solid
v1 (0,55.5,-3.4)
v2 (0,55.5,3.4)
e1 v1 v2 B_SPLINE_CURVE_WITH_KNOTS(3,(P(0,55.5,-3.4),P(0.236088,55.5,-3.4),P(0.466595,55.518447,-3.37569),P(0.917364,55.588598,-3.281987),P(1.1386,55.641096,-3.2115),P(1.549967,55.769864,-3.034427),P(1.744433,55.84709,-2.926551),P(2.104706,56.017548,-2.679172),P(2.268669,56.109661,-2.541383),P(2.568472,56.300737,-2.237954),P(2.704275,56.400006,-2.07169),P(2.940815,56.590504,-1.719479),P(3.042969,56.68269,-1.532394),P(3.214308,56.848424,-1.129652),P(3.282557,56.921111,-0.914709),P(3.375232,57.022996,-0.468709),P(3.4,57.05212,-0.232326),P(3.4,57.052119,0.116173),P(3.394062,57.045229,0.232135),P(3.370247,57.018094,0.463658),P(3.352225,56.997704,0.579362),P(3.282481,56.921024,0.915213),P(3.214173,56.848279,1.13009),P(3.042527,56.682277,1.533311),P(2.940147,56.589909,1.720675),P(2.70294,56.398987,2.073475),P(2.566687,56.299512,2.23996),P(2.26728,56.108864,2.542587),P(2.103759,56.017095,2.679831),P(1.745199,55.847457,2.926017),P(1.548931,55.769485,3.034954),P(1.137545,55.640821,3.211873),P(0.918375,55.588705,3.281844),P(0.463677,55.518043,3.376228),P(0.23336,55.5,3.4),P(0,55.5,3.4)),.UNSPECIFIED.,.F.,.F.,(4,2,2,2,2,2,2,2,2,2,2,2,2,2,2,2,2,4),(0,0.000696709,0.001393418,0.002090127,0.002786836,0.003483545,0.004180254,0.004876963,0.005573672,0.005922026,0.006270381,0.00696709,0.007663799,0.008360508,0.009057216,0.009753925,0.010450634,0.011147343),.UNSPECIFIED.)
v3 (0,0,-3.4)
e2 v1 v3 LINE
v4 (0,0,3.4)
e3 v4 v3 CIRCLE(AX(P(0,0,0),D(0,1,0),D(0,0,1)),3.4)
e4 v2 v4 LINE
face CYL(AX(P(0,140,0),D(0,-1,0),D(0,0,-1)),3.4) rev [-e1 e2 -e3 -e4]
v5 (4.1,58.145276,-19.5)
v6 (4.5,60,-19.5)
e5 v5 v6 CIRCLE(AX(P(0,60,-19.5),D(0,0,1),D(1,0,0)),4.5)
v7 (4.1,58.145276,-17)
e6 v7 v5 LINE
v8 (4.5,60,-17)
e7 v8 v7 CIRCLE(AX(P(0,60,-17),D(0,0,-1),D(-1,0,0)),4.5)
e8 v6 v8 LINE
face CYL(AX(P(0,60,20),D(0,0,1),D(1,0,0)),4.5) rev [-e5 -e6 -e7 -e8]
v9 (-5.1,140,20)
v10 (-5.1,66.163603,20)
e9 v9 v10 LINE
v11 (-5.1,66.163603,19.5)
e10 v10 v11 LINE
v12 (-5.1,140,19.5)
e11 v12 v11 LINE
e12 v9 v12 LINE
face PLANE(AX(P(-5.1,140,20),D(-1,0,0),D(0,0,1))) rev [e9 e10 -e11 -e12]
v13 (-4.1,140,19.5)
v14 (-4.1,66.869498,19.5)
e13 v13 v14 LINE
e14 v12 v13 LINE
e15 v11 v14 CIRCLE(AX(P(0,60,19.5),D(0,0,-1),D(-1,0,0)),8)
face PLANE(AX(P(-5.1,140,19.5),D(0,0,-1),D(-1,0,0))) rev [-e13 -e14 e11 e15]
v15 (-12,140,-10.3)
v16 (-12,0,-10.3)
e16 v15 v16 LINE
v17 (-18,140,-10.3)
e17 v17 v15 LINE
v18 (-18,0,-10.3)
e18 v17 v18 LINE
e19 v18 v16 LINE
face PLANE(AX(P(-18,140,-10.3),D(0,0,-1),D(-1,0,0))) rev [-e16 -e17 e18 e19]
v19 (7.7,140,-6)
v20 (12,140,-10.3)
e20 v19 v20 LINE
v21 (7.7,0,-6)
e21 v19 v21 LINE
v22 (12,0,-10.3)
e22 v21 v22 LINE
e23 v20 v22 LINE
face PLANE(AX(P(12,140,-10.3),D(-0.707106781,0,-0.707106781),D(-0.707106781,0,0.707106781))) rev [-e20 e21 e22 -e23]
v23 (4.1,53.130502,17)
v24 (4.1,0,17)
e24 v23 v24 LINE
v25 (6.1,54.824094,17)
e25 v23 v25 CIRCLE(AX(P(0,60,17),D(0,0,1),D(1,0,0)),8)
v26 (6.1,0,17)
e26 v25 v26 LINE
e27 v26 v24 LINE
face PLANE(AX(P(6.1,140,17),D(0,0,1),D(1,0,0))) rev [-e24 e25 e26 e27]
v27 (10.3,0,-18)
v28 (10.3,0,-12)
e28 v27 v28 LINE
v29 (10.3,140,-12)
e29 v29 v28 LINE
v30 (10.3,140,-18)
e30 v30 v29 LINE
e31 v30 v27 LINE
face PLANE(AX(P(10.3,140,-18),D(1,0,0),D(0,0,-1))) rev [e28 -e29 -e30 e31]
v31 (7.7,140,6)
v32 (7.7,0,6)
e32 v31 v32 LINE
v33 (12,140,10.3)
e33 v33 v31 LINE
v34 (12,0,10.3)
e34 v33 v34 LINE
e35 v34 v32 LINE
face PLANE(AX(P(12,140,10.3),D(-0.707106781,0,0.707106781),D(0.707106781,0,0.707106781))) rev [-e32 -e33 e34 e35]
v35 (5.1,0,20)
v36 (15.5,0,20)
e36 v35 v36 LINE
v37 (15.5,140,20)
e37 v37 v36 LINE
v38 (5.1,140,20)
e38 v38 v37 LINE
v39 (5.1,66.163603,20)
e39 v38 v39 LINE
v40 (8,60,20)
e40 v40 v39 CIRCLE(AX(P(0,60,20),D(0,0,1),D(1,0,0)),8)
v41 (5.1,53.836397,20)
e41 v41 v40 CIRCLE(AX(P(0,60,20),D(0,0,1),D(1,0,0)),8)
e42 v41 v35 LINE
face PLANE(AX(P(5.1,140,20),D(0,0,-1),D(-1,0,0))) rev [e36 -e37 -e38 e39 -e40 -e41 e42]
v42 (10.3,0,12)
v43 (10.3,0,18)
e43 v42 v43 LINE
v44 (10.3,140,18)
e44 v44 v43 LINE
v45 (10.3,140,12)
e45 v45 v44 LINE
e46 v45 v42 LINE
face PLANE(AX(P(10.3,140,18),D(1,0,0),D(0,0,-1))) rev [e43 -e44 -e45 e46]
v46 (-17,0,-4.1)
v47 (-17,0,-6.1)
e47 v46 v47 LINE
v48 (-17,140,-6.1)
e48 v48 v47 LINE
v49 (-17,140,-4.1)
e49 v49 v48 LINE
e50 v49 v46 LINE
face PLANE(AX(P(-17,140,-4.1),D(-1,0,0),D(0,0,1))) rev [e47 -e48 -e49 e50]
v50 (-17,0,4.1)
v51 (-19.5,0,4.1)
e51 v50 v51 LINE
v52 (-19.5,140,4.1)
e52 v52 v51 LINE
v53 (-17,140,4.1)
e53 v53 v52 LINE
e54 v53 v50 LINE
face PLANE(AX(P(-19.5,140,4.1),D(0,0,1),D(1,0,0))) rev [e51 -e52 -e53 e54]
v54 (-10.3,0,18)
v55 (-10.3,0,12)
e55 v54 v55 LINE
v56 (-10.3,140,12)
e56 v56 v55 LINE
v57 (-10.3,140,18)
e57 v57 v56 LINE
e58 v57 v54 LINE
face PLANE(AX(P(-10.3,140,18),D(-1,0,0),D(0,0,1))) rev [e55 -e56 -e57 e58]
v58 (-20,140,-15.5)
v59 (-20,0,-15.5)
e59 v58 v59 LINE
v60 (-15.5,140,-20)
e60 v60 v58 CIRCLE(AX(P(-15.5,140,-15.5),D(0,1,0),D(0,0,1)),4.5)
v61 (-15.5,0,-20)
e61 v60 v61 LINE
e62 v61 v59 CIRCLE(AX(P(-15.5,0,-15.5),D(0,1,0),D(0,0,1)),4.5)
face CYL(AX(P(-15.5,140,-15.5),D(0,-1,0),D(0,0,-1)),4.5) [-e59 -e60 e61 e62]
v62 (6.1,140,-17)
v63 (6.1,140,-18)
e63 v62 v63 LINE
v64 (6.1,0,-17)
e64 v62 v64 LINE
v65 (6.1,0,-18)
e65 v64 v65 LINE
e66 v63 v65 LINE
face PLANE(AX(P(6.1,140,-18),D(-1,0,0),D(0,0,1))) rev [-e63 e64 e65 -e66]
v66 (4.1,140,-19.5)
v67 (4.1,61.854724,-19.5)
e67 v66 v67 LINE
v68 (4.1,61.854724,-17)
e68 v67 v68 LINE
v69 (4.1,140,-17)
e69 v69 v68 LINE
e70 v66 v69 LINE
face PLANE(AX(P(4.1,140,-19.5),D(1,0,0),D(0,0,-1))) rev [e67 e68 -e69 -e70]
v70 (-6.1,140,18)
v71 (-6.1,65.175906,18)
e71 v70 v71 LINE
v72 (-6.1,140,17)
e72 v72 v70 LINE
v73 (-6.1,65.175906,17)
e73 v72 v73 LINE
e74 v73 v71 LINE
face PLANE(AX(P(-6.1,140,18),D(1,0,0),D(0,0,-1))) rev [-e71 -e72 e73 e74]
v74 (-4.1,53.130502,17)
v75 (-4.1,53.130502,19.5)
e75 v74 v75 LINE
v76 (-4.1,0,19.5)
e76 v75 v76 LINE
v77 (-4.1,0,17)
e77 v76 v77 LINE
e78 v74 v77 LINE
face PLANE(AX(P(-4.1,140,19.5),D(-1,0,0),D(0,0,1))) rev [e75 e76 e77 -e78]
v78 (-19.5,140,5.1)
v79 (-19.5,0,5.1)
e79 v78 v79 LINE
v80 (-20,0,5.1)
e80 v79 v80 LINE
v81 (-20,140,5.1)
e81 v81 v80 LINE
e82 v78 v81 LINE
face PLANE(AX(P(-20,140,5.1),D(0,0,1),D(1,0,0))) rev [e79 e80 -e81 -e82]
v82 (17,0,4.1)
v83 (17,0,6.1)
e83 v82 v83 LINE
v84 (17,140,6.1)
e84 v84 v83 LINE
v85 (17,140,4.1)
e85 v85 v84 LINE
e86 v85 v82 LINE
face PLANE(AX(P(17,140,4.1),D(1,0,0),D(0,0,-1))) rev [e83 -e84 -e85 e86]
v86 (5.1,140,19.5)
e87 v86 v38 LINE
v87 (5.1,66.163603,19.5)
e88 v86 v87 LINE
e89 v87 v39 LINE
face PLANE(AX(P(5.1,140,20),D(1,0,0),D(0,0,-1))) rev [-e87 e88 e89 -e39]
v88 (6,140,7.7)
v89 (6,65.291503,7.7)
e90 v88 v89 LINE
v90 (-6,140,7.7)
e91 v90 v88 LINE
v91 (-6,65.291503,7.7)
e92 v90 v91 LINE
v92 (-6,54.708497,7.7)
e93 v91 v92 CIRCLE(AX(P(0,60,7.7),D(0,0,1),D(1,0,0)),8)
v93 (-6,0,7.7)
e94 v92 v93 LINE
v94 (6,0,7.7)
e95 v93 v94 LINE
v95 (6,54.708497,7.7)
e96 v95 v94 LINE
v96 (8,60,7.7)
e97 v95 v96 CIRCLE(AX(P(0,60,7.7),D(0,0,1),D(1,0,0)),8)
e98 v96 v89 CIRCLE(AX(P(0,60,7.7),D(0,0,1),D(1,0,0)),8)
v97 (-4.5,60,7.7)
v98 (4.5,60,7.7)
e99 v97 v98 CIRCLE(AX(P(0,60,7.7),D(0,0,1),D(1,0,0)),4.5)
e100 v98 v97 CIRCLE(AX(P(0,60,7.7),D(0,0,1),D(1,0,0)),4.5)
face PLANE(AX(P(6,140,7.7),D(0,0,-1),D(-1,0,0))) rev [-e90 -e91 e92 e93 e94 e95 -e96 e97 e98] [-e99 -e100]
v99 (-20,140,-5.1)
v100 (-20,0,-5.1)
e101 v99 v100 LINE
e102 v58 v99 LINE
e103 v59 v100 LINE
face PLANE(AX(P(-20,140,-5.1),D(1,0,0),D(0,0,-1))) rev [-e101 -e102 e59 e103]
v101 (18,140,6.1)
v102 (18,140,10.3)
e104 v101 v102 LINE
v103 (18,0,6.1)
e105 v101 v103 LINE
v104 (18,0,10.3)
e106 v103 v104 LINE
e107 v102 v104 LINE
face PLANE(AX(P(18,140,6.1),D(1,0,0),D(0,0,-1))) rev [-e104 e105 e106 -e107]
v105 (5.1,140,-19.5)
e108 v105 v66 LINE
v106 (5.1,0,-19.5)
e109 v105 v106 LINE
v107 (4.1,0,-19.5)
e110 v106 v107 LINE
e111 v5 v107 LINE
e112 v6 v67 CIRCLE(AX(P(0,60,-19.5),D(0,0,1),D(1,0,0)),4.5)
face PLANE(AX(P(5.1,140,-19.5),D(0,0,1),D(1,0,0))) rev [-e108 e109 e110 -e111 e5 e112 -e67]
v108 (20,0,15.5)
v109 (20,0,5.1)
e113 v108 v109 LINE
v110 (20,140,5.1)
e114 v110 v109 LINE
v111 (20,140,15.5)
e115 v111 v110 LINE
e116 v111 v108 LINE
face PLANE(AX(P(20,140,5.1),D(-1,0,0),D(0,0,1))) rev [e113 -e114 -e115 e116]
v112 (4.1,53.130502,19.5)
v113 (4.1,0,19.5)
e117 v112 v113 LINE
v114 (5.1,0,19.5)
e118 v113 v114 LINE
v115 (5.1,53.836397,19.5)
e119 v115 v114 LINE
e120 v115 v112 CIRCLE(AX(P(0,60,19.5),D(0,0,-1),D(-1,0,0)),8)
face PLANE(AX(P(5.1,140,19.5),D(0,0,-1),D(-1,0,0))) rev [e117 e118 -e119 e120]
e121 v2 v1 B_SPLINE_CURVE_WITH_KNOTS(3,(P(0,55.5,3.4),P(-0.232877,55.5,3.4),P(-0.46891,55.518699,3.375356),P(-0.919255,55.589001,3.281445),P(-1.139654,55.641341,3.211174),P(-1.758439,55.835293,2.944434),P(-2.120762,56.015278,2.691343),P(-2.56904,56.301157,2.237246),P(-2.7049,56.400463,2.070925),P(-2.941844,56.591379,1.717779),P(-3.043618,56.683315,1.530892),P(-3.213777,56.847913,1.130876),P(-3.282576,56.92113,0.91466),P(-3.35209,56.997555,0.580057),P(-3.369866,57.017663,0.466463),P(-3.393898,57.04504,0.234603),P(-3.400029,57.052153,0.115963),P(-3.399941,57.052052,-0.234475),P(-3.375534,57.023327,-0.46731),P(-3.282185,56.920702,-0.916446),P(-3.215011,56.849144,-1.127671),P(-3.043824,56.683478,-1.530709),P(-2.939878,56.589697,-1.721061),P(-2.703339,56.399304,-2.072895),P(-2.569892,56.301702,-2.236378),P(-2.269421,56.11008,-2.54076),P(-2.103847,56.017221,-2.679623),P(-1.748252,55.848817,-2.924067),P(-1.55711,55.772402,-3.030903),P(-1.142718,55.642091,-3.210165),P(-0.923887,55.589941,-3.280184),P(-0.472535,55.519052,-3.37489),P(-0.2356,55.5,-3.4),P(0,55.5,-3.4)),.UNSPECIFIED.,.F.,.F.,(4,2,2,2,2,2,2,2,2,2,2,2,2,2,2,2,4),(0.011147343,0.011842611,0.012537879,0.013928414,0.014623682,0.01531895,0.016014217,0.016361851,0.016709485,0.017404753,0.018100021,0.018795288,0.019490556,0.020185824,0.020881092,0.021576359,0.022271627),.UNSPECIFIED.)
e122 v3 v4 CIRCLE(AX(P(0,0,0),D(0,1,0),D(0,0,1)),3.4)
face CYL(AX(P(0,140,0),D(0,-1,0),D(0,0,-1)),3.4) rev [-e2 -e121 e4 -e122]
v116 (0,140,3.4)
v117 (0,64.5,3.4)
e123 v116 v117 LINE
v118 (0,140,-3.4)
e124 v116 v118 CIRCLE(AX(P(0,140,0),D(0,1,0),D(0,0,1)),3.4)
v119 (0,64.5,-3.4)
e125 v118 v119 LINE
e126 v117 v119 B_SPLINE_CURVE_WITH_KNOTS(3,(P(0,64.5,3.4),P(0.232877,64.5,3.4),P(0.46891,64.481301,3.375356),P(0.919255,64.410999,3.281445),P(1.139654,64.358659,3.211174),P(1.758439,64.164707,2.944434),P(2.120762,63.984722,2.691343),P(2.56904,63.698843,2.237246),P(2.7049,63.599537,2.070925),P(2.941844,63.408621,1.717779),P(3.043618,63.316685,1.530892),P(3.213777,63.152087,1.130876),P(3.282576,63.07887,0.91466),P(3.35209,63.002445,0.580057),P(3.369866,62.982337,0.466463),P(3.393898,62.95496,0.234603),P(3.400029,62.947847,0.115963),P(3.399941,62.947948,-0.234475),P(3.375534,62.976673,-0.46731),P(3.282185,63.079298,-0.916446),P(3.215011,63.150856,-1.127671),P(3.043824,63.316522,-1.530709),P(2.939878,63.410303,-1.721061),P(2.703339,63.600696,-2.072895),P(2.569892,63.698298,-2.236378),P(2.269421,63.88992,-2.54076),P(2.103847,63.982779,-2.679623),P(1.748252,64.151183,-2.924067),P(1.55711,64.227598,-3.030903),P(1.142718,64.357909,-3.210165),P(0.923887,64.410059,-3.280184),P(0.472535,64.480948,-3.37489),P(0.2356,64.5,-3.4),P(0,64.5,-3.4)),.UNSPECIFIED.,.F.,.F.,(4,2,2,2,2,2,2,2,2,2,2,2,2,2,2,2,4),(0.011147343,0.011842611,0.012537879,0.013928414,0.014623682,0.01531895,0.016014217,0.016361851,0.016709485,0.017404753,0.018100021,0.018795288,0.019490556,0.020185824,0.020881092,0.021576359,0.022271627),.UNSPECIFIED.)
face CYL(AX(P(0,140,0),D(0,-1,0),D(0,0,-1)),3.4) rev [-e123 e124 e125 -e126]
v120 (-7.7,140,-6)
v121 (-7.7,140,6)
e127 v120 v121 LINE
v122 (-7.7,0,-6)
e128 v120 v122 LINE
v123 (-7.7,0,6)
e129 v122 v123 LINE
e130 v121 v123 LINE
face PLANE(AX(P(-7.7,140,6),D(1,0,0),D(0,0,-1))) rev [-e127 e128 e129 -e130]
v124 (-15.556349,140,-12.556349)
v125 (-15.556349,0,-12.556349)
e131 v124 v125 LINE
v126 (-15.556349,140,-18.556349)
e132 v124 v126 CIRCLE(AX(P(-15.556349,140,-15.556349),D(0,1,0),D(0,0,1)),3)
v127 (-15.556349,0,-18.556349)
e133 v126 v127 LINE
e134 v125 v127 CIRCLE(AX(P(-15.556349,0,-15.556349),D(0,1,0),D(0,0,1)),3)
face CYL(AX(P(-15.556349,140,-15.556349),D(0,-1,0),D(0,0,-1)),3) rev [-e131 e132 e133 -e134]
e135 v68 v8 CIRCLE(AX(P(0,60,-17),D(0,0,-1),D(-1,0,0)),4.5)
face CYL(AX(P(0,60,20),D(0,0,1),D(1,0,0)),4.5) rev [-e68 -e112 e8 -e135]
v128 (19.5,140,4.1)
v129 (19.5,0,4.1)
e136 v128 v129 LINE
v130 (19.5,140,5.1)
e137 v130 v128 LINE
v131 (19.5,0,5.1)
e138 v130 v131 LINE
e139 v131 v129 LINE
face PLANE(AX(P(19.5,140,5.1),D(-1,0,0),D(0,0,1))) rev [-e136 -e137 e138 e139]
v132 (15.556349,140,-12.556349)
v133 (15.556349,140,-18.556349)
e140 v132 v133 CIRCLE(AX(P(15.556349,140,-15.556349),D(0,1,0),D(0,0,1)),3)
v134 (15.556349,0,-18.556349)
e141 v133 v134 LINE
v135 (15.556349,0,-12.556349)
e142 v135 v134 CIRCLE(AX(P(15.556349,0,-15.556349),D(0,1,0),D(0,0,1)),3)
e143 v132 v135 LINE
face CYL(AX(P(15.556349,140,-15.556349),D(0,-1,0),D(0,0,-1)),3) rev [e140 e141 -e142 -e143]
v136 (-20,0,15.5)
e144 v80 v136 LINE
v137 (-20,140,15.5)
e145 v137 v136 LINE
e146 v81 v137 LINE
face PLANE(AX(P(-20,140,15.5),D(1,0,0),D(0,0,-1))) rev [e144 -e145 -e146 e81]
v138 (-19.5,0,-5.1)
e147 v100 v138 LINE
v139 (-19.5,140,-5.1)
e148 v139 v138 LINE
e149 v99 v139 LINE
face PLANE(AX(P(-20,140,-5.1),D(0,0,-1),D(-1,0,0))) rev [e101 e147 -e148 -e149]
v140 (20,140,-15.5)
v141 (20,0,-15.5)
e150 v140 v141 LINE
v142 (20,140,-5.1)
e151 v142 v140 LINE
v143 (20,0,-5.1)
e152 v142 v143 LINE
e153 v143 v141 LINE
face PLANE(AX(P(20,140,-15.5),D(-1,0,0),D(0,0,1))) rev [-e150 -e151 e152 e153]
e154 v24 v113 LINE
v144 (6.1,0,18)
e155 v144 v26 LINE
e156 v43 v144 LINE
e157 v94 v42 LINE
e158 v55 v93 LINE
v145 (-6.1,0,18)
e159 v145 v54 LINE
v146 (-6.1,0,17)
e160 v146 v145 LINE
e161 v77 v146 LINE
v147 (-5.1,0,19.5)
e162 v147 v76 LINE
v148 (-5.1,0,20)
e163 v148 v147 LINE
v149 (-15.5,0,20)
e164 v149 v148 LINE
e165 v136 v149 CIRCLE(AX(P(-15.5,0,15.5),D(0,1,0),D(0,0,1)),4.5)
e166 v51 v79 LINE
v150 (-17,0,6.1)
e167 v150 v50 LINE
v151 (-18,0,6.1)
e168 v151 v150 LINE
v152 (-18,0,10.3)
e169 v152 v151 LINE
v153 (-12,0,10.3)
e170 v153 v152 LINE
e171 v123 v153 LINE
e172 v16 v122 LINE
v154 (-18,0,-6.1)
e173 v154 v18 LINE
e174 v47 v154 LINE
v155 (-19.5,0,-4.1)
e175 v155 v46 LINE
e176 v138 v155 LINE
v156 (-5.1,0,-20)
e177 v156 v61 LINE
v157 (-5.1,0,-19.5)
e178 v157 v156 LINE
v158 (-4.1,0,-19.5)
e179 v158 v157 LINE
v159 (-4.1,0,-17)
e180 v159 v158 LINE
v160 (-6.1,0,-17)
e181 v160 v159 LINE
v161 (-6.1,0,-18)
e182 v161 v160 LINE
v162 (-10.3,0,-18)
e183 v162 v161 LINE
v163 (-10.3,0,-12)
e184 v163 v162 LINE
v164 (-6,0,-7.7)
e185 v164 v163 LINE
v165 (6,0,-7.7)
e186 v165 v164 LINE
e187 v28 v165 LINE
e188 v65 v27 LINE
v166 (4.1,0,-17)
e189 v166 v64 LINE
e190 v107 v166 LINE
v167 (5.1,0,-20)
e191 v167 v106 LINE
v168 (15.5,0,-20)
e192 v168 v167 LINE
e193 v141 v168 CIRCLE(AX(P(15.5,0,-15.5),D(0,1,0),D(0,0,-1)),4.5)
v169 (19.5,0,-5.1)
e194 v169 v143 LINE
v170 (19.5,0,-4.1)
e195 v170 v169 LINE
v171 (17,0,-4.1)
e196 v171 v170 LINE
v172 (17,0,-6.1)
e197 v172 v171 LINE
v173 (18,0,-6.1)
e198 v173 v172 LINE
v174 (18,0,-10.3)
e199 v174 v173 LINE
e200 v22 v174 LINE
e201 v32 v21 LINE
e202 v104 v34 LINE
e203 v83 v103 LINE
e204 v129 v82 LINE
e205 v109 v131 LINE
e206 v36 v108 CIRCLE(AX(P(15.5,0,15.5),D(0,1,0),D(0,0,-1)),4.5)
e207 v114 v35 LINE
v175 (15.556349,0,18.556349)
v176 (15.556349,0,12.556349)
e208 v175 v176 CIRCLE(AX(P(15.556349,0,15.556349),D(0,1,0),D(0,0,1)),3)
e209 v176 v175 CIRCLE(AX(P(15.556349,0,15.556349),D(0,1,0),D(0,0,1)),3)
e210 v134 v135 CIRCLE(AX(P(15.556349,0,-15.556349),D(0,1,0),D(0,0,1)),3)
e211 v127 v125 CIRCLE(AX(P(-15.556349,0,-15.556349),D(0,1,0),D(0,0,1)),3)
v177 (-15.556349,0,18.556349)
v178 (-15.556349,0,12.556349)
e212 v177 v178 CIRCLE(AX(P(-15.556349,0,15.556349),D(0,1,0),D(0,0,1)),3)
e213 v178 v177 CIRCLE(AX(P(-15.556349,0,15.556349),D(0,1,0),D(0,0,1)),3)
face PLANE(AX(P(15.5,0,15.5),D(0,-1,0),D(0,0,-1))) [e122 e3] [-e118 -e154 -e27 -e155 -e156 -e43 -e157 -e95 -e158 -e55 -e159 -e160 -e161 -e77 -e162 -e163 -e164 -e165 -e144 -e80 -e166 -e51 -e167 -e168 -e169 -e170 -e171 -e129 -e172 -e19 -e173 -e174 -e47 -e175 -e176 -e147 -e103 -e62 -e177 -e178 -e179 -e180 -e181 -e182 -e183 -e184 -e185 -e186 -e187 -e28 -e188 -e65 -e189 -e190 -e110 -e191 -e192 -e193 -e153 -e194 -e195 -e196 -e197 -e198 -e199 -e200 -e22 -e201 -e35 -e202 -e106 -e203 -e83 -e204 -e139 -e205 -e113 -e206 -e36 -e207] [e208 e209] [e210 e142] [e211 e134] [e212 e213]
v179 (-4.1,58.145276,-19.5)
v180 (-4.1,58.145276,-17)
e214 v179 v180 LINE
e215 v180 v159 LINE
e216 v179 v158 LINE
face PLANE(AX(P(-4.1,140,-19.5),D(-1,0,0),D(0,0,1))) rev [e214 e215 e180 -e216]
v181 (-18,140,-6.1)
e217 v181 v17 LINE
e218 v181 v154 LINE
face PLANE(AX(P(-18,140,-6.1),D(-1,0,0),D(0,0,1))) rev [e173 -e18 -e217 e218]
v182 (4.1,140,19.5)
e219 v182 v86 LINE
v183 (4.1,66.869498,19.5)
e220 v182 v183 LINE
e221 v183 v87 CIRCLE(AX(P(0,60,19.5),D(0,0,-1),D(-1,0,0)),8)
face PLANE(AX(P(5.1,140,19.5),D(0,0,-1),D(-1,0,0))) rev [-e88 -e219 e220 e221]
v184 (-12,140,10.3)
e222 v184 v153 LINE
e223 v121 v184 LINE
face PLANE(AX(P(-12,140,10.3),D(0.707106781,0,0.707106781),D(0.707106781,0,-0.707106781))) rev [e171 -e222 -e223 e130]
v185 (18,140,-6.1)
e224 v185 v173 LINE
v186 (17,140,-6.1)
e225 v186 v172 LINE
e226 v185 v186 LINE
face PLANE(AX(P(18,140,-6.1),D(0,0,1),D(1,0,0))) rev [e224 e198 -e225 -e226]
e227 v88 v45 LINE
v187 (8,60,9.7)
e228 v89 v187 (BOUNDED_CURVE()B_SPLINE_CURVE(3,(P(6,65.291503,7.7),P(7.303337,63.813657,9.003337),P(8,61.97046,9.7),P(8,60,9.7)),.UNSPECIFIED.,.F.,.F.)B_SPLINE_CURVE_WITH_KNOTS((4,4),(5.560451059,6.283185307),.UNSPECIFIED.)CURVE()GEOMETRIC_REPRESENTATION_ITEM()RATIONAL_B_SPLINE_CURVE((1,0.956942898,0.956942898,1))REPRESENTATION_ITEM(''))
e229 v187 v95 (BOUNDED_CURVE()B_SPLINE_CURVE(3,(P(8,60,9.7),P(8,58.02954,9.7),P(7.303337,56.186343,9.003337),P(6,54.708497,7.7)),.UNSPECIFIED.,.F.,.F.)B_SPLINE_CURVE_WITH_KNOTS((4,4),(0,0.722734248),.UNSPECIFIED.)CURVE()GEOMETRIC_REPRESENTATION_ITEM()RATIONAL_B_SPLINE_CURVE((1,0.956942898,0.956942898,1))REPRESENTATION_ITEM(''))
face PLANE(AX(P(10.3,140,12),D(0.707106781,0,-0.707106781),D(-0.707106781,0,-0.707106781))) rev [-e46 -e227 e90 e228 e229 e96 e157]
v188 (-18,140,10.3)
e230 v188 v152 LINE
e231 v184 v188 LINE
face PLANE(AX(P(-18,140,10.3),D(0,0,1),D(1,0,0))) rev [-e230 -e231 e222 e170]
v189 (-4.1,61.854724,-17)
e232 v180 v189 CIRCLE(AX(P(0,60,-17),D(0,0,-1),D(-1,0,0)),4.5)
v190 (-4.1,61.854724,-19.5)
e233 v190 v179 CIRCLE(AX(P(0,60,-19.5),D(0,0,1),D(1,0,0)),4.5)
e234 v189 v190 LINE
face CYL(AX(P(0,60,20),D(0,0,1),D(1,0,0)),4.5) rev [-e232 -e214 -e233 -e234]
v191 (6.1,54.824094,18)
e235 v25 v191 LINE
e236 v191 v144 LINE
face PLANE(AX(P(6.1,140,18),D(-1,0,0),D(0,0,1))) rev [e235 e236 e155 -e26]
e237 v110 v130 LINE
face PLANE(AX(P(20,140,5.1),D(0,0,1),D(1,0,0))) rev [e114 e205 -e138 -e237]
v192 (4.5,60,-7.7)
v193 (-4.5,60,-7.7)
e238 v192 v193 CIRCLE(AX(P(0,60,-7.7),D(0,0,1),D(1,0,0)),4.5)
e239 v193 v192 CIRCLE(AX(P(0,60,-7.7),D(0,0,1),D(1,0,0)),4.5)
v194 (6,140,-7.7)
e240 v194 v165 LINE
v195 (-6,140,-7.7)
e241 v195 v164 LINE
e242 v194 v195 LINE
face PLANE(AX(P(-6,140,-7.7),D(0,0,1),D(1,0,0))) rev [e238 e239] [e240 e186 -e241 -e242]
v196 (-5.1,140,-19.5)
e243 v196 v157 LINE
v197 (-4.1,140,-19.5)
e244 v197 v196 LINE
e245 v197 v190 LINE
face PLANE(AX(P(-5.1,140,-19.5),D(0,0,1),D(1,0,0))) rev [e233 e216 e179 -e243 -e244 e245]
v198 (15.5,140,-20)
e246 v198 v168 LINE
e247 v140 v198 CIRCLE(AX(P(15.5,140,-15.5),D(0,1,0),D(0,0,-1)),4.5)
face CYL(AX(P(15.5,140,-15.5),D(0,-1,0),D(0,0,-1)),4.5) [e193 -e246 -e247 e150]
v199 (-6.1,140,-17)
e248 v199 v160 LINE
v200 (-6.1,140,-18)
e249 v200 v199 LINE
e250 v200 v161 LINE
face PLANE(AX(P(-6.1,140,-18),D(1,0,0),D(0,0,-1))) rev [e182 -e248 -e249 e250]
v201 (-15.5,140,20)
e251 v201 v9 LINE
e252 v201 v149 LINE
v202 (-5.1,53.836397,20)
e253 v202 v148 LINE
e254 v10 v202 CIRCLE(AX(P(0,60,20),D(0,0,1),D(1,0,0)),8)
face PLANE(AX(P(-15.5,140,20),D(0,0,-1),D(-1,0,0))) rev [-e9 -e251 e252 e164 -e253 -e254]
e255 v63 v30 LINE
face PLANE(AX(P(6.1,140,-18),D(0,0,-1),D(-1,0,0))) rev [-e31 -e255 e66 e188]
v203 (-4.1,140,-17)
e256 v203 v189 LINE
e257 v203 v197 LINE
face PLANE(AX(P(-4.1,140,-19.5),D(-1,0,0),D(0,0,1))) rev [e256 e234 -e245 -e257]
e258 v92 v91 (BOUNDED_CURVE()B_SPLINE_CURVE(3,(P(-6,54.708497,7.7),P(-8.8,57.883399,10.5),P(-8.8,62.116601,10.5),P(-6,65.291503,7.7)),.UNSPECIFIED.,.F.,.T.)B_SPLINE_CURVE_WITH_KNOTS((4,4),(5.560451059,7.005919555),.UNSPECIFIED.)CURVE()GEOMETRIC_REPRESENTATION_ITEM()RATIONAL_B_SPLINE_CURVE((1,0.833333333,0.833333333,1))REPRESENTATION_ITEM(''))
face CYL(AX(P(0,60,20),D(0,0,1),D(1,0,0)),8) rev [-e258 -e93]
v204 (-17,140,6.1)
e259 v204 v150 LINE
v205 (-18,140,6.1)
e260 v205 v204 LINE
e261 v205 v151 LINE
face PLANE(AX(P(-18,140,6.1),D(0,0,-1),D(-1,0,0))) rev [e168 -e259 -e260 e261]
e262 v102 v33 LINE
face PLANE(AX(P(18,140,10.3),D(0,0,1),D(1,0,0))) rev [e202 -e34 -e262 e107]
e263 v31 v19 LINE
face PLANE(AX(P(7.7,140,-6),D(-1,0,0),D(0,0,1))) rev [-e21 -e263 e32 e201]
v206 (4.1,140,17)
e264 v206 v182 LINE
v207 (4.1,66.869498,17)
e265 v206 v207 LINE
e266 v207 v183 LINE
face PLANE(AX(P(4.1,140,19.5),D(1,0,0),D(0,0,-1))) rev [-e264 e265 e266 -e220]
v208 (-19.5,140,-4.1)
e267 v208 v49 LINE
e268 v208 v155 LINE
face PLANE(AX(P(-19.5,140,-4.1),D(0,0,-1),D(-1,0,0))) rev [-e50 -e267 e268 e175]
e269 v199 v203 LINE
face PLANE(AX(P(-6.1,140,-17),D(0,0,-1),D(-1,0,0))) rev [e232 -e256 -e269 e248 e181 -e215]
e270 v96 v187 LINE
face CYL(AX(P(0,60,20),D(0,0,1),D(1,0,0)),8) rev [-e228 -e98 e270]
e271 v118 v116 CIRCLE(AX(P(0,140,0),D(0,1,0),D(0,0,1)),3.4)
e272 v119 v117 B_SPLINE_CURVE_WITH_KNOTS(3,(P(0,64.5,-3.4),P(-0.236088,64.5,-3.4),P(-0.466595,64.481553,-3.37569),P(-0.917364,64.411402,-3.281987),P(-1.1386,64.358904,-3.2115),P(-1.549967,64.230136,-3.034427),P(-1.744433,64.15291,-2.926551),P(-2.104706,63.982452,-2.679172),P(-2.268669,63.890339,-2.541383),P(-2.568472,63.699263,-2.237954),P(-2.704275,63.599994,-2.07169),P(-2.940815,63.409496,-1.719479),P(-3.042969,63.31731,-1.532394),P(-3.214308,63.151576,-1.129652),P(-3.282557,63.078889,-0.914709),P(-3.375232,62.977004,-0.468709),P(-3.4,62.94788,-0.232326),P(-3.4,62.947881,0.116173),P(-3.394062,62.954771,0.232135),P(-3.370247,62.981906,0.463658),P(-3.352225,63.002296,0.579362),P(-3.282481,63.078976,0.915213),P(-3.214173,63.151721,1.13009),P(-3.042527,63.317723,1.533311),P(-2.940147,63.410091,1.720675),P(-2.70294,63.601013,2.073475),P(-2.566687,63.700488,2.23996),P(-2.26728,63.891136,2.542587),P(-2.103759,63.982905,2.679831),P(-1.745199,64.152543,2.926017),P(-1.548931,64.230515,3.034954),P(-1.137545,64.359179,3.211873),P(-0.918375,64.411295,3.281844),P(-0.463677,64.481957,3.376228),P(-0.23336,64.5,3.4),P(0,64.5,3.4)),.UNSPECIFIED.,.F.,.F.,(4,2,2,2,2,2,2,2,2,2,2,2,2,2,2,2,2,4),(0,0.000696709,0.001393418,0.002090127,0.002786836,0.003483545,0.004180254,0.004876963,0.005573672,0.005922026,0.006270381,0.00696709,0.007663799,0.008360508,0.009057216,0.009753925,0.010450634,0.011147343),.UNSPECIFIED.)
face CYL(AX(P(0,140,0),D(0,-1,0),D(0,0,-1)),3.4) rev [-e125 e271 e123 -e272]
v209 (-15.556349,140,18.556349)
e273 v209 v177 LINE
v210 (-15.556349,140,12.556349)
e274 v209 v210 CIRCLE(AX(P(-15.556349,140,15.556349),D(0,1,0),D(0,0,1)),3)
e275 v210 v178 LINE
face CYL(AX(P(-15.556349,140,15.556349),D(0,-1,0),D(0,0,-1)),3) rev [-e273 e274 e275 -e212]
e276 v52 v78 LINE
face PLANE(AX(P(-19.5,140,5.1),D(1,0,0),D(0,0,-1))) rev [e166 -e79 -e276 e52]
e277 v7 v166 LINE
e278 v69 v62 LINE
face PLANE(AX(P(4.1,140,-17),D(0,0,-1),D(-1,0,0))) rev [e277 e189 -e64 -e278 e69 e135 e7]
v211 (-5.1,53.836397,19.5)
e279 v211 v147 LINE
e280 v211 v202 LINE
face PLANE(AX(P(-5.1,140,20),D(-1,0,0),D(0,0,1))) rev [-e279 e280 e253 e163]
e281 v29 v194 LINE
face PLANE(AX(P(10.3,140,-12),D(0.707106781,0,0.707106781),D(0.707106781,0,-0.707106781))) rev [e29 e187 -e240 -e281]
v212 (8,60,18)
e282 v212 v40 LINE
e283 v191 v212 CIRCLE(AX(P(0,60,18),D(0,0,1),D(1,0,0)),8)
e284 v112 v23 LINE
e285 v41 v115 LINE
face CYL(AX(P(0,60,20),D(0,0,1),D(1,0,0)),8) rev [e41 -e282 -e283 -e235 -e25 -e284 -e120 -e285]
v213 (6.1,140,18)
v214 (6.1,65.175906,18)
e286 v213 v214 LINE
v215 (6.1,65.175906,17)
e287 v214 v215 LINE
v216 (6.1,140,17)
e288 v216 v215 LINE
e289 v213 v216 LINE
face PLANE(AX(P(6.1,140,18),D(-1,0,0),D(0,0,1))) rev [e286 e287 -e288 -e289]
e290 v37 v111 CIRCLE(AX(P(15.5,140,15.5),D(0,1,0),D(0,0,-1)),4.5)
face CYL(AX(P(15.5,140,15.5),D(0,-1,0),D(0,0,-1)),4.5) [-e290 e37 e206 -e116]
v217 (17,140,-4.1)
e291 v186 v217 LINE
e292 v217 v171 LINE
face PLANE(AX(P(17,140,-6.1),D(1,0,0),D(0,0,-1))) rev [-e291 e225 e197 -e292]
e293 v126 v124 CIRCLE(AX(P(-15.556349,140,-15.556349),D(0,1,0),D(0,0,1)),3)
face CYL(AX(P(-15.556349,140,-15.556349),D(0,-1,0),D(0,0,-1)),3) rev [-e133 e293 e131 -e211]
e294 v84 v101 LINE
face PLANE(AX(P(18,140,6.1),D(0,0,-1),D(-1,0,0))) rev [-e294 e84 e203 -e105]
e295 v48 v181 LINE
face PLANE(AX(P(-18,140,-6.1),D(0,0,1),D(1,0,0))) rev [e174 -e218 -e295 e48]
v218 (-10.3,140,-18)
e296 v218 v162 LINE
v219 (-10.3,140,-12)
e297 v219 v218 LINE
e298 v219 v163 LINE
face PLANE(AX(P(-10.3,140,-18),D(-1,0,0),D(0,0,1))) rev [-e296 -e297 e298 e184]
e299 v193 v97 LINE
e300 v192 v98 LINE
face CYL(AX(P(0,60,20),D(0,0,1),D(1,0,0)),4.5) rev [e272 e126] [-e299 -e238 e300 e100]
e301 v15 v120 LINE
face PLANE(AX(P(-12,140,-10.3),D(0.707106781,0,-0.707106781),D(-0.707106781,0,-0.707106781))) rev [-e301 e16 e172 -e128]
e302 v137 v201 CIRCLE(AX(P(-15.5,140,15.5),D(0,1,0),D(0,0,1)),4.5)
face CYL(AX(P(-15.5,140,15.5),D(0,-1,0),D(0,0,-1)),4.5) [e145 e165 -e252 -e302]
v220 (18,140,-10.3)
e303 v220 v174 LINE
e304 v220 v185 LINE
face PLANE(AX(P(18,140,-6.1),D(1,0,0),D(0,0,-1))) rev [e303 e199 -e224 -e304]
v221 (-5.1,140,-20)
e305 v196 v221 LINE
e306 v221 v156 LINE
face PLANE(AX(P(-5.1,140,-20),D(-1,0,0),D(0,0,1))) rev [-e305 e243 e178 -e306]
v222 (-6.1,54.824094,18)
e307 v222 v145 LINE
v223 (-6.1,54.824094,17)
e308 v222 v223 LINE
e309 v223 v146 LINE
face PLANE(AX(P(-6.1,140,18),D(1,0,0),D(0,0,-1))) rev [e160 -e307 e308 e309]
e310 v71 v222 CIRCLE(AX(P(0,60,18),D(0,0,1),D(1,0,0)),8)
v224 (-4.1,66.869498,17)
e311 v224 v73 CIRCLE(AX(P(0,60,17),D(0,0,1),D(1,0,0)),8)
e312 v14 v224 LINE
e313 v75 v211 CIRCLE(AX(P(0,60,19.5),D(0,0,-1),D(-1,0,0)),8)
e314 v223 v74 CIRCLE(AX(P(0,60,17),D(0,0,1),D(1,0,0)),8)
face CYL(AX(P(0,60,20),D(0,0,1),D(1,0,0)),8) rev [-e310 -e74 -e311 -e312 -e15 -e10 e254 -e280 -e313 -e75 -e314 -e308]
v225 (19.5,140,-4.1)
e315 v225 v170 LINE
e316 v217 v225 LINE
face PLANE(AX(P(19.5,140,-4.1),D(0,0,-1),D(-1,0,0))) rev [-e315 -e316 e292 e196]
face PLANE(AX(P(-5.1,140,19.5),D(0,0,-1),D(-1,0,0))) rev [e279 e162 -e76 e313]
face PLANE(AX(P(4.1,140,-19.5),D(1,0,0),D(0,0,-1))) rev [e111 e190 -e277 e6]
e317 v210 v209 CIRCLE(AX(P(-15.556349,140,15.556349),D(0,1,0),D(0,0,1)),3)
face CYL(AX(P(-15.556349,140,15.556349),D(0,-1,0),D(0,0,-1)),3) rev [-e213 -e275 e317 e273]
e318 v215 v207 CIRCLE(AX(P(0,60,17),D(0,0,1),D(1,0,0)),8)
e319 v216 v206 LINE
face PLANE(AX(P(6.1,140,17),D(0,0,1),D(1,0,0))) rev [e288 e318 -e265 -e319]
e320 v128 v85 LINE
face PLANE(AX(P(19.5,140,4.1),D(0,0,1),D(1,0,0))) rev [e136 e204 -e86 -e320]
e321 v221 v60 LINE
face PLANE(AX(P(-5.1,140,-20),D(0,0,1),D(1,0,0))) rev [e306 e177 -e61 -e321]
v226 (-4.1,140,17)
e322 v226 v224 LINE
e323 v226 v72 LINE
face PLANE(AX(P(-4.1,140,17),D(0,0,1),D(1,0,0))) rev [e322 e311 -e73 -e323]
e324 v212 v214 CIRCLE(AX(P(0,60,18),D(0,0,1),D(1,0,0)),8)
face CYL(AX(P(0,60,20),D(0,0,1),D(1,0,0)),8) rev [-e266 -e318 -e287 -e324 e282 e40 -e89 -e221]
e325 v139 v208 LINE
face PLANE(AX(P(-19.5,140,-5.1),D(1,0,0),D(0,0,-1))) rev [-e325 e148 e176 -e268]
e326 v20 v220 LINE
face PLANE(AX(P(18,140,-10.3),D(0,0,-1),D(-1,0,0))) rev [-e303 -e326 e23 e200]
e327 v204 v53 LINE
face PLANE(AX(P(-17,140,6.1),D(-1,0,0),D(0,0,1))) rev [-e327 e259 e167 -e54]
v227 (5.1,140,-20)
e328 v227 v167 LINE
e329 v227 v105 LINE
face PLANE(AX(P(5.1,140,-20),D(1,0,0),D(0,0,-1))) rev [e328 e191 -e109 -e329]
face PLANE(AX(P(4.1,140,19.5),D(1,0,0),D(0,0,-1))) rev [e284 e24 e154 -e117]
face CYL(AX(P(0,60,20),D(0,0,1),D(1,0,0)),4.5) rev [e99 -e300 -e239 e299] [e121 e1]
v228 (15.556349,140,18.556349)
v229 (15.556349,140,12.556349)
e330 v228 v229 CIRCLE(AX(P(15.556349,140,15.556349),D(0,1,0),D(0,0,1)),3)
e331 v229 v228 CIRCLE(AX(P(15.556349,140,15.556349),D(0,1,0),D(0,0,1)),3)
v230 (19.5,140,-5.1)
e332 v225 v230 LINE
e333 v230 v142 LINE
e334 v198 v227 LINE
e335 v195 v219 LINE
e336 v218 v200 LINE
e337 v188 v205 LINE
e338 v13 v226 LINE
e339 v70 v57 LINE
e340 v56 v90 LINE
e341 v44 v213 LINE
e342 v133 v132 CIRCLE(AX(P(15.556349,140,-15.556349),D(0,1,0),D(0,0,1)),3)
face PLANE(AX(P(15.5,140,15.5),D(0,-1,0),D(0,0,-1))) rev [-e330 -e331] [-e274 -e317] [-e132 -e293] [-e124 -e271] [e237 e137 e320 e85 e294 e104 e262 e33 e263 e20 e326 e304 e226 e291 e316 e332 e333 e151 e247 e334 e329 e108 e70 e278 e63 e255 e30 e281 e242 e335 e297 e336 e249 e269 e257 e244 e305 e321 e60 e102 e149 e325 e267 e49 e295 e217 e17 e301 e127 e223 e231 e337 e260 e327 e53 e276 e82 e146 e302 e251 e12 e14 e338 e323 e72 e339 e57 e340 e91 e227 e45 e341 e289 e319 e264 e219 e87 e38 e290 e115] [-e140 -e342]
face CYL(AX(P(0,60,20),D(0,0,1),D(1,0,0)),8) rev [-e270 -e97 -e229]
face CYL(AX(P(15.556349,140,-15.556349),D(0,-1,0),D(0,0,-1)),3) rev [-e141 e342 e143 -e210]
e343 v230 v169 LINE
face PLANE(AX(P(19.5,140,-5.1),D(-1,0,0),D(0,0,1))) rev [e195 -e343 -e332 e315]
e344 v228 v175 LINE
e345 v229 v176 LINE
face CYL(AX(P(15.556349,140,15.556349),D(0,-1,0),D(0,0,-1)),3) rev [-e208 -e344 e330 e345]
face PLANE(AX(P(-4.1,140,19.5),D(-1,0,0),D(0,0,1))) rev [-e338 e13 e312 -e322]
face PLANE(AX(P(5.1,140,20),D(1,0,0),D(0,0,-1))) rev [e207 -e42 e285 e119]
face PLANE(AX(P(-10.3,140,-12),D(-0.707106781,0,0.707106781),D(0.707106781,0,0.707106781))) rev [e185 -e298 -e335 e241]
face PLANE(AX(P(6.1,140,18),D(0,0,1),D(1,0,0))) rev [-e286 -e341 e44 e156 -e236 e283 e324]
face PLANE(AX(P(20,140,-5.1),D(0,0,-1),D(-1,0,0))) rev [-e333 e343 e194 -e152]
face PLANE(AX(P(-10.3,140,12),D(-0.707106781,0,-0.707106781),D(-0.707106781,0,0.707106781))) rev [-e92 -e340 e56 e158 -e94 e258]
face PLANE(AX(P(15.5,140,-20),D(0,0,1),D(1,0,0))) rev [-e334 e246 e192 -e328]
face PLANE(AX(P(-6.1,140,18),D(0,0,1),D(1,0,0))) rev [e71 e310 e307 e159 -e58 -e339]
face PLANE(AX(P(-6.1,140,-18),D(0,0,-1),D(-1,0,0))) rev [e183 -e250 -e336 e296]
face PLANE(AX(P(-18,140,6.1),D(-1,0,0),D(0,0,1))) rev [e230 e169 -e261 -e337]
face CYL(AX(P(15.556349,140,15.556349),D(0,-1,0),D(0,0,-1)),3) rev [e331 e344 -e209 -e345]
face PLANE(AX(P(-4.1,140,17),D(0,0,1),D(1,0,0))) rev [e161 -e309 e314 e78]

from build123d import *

# Parameters (mm, degrees)
SKETCH16_R                   = 3.4
SKETCH16_R_2                 = 3
MEMBER_1_DEPTH               = 140
HOLE_WIZARD_M8_1_D           = 9
HOLE_WIZARD_M8_1_CBORE_D     = 16
HOLE_WIZARD_M8_1_CBORE_DEPTH = 12.3


with BuildPart() as part:
    # Sketch16 → Member 1 (new body)
    with BuildSketch(Plane(origin=(0, 0, 0), x_dir=(-1, 0, 0), z_dir=(0, 1, 0))):
        with BuildLine():
            Line((-5.1, 20), (-5.1, 19.5))
            Line((-5.1, 19.5), (-4.1, 19.5))
            Line((-4.1, 19.5), (-4.1, 17))
            Line((-4.1, 17), (-6.1, 17))
            Line((-6.1, 17), (-6.1, 18))
            Line((-6.1, 18), (-10.3, 18))
            Line((-10.3, 18), (-10.3, 12))
            Line((-10.3, 12), (-6, 7.7))
            Line((-6, 7.7), (6, 7.7))
            Line((6, 7.7), (10.3, 12))
            Line((10.3, 12), (10.3, 18))
            Line((10.3, 18), (6.1, 18))
            Line((6.1, 18), (6.1, 17))
            Line((6.1, 17), (4.1, 17))
            Line((4.1, 17), (4.1, 19.5))
            Line((4.1, 19.5), (5.1, 19.5))
            Line((5.1, 19.5), (5.1, 20))
            Line((5.1, 20), (15.5, 20))
            ThreePointArc((15.5, 20), (18.681980515, 18.681980515), (20, 15.5))
            Line((20, 15.5), (20, 5.1))
            Line((20, 5.1), (19.5, 5.1))
            Line((19.5, 5.1), (19.5, 4.1))
            Line((19.5, 4.1), (17, 4.1))
            Line((17, 4.1), (17, 6.1))
            Line((17, 6.1), (18, 6.1))
            Line((18, 6.1), (18, 10.3))
            Line((18, 10.3), (12, 10.3))
            Line((12, 10.3), (7.7, 6))
            Line((7.7, 6), (7.7, -6))
            Line((7.7, -6), (12, -10.3))
            Line((12, -10.3), (18, -10.3))
            Line((18, -10.3), (18, -6.1))
            Line((18, -6.1), (17, -6.1))
            Line((17, -6.1), (17, -4.1))
            Line((17, -4.1), (19.5, -4.1))
            Line((19.5, -4.1), (19.5, -5.1))
            Line((19.5, -5.1), (20, -5.1))
            Line((20, -5.1), (20, -15.5))
            ThreePointArc((20, -15.5), (18.681980515, -18.681980515), (15.5, -20))
            Line((15.5, -20), (5.1, -20))
            Line((5.1, -20), (5.1, -19.5))
            Line((5.1, -19.5), (4.1, -19.5))
            Line((4.1, -19.5), (4.1, -17))
            Line((4.1, -17), (6.1, -17))
            Line((6.1, -17), (6.1, -18))
            Line((6.1, -18), (10.3, -18))
            Line((10.3, -18), (10.3, -12))
            Line((10.3, -12), (6, -7.7))
            Line((6, -7.7), (-6, -7.7))
            Line((-6, -7.7), (-10.3, -12))
            Line((-10.3, -12), (-10.3, -18))
            Line((-10.3, -18), (-6.1, -18))
            Line((-6.1, -18), (-6.1, -17))
            Line((-6.1, -17), (-4.1, -17))
            Line((-4.1, -17), (-4.1, -19.5))
            Line((-4.1, -19.5), (-5.1, -19.5))
            Line((-5.1, -19.5), (-5.1, -20))
            Line((-5.1, -20), (-15.5, -20))
            ThreePointArc((-15.5, -20), (-18.681980515, -18.681980515), (-20, -15.5))
            Line((-20, -15.5), (-20, -5.1))
            Line((-20, -5.1), (-19.5, -5.1))
            Line((-19.5, -5.1), (-19.5, -4.1))
            Line((-19.5, -4.1), (-17, -4.1))
            Line((-17, -4.1), (-17, -6.1))
            Line((-17, -6.1), (-18, -6.1))
            Line((-18, -6.1), (-18, -10.3))
            Line((-18, -10.3), (-12, -10.3))
            Line((-12, -10.3), (-7.7, -6))
            Line((-7.7, -6), (-7.7, 6))
            Line((-7.7, 6), (-12, 10.3))
            Line((-12, 10.3), (-18, 10.3))
            Line((-18, 10.3), (-18, 6.1))
            Line((-18, 6.1), (-17, 6.1))
            Line((-17, 6.1), (-17, 4.1))
            Line((-17, 4.1), (-19.5, 4.1))
            Line((-19.5, 4.1), (-19.5, 5.1))
            Line((-19.5, 5.1), (-20, 5.1))
            Line((-20, 5.1), (-20, 15.5))
            ThreePointArc((-20, 15.5), (-18.681980515, 18.681980515), (-15.5, 20))
            Line((-15.5, 20), (-5.1, 20))
        make_face()
        Circle(SKETCH16_R, mode=Mode.SUBTRACT)
        with Locations((-15.556349186, 15.556349186)):
            Circle(SKETCH16_R_2, mode=Mode.SUBTRACT)
        with Locations((15.556349186, 15.556349186)):
            Circle(SKETCH16_R_2, mode=Mode.SUBTRACT)
        with Locations((15.556349186, -15.556349186)):
            Circle(SKETCH16_R_2, mode=Mode.SUBTRACT)
        with Locations((-15.556349186, -15.556349186)):
            Circle(SKETCH16_R_2, mode=Mode.SUBTRACT)
    extrude(amount=MEMBER_1_DEPTH)

    # M8 六角凹头螺钉的柱形沉头孔1 (through all)
    with Locations(Plane(origin=(9.58186976, -44.093066006, 20), x_dir=(-1, 0, 0), z_dir=(0, 0, 1))):
        with Locations((9.58186976, -104.093066006)):
            CounterBoreHole(HOLE_WIZARD_M8_1_D / 2, HOLE_WIZARD_M8_1_CBORE_D / 2, HOLE_WIZARD_M8_1_CBORE_DEPTH)


solid = part.part
